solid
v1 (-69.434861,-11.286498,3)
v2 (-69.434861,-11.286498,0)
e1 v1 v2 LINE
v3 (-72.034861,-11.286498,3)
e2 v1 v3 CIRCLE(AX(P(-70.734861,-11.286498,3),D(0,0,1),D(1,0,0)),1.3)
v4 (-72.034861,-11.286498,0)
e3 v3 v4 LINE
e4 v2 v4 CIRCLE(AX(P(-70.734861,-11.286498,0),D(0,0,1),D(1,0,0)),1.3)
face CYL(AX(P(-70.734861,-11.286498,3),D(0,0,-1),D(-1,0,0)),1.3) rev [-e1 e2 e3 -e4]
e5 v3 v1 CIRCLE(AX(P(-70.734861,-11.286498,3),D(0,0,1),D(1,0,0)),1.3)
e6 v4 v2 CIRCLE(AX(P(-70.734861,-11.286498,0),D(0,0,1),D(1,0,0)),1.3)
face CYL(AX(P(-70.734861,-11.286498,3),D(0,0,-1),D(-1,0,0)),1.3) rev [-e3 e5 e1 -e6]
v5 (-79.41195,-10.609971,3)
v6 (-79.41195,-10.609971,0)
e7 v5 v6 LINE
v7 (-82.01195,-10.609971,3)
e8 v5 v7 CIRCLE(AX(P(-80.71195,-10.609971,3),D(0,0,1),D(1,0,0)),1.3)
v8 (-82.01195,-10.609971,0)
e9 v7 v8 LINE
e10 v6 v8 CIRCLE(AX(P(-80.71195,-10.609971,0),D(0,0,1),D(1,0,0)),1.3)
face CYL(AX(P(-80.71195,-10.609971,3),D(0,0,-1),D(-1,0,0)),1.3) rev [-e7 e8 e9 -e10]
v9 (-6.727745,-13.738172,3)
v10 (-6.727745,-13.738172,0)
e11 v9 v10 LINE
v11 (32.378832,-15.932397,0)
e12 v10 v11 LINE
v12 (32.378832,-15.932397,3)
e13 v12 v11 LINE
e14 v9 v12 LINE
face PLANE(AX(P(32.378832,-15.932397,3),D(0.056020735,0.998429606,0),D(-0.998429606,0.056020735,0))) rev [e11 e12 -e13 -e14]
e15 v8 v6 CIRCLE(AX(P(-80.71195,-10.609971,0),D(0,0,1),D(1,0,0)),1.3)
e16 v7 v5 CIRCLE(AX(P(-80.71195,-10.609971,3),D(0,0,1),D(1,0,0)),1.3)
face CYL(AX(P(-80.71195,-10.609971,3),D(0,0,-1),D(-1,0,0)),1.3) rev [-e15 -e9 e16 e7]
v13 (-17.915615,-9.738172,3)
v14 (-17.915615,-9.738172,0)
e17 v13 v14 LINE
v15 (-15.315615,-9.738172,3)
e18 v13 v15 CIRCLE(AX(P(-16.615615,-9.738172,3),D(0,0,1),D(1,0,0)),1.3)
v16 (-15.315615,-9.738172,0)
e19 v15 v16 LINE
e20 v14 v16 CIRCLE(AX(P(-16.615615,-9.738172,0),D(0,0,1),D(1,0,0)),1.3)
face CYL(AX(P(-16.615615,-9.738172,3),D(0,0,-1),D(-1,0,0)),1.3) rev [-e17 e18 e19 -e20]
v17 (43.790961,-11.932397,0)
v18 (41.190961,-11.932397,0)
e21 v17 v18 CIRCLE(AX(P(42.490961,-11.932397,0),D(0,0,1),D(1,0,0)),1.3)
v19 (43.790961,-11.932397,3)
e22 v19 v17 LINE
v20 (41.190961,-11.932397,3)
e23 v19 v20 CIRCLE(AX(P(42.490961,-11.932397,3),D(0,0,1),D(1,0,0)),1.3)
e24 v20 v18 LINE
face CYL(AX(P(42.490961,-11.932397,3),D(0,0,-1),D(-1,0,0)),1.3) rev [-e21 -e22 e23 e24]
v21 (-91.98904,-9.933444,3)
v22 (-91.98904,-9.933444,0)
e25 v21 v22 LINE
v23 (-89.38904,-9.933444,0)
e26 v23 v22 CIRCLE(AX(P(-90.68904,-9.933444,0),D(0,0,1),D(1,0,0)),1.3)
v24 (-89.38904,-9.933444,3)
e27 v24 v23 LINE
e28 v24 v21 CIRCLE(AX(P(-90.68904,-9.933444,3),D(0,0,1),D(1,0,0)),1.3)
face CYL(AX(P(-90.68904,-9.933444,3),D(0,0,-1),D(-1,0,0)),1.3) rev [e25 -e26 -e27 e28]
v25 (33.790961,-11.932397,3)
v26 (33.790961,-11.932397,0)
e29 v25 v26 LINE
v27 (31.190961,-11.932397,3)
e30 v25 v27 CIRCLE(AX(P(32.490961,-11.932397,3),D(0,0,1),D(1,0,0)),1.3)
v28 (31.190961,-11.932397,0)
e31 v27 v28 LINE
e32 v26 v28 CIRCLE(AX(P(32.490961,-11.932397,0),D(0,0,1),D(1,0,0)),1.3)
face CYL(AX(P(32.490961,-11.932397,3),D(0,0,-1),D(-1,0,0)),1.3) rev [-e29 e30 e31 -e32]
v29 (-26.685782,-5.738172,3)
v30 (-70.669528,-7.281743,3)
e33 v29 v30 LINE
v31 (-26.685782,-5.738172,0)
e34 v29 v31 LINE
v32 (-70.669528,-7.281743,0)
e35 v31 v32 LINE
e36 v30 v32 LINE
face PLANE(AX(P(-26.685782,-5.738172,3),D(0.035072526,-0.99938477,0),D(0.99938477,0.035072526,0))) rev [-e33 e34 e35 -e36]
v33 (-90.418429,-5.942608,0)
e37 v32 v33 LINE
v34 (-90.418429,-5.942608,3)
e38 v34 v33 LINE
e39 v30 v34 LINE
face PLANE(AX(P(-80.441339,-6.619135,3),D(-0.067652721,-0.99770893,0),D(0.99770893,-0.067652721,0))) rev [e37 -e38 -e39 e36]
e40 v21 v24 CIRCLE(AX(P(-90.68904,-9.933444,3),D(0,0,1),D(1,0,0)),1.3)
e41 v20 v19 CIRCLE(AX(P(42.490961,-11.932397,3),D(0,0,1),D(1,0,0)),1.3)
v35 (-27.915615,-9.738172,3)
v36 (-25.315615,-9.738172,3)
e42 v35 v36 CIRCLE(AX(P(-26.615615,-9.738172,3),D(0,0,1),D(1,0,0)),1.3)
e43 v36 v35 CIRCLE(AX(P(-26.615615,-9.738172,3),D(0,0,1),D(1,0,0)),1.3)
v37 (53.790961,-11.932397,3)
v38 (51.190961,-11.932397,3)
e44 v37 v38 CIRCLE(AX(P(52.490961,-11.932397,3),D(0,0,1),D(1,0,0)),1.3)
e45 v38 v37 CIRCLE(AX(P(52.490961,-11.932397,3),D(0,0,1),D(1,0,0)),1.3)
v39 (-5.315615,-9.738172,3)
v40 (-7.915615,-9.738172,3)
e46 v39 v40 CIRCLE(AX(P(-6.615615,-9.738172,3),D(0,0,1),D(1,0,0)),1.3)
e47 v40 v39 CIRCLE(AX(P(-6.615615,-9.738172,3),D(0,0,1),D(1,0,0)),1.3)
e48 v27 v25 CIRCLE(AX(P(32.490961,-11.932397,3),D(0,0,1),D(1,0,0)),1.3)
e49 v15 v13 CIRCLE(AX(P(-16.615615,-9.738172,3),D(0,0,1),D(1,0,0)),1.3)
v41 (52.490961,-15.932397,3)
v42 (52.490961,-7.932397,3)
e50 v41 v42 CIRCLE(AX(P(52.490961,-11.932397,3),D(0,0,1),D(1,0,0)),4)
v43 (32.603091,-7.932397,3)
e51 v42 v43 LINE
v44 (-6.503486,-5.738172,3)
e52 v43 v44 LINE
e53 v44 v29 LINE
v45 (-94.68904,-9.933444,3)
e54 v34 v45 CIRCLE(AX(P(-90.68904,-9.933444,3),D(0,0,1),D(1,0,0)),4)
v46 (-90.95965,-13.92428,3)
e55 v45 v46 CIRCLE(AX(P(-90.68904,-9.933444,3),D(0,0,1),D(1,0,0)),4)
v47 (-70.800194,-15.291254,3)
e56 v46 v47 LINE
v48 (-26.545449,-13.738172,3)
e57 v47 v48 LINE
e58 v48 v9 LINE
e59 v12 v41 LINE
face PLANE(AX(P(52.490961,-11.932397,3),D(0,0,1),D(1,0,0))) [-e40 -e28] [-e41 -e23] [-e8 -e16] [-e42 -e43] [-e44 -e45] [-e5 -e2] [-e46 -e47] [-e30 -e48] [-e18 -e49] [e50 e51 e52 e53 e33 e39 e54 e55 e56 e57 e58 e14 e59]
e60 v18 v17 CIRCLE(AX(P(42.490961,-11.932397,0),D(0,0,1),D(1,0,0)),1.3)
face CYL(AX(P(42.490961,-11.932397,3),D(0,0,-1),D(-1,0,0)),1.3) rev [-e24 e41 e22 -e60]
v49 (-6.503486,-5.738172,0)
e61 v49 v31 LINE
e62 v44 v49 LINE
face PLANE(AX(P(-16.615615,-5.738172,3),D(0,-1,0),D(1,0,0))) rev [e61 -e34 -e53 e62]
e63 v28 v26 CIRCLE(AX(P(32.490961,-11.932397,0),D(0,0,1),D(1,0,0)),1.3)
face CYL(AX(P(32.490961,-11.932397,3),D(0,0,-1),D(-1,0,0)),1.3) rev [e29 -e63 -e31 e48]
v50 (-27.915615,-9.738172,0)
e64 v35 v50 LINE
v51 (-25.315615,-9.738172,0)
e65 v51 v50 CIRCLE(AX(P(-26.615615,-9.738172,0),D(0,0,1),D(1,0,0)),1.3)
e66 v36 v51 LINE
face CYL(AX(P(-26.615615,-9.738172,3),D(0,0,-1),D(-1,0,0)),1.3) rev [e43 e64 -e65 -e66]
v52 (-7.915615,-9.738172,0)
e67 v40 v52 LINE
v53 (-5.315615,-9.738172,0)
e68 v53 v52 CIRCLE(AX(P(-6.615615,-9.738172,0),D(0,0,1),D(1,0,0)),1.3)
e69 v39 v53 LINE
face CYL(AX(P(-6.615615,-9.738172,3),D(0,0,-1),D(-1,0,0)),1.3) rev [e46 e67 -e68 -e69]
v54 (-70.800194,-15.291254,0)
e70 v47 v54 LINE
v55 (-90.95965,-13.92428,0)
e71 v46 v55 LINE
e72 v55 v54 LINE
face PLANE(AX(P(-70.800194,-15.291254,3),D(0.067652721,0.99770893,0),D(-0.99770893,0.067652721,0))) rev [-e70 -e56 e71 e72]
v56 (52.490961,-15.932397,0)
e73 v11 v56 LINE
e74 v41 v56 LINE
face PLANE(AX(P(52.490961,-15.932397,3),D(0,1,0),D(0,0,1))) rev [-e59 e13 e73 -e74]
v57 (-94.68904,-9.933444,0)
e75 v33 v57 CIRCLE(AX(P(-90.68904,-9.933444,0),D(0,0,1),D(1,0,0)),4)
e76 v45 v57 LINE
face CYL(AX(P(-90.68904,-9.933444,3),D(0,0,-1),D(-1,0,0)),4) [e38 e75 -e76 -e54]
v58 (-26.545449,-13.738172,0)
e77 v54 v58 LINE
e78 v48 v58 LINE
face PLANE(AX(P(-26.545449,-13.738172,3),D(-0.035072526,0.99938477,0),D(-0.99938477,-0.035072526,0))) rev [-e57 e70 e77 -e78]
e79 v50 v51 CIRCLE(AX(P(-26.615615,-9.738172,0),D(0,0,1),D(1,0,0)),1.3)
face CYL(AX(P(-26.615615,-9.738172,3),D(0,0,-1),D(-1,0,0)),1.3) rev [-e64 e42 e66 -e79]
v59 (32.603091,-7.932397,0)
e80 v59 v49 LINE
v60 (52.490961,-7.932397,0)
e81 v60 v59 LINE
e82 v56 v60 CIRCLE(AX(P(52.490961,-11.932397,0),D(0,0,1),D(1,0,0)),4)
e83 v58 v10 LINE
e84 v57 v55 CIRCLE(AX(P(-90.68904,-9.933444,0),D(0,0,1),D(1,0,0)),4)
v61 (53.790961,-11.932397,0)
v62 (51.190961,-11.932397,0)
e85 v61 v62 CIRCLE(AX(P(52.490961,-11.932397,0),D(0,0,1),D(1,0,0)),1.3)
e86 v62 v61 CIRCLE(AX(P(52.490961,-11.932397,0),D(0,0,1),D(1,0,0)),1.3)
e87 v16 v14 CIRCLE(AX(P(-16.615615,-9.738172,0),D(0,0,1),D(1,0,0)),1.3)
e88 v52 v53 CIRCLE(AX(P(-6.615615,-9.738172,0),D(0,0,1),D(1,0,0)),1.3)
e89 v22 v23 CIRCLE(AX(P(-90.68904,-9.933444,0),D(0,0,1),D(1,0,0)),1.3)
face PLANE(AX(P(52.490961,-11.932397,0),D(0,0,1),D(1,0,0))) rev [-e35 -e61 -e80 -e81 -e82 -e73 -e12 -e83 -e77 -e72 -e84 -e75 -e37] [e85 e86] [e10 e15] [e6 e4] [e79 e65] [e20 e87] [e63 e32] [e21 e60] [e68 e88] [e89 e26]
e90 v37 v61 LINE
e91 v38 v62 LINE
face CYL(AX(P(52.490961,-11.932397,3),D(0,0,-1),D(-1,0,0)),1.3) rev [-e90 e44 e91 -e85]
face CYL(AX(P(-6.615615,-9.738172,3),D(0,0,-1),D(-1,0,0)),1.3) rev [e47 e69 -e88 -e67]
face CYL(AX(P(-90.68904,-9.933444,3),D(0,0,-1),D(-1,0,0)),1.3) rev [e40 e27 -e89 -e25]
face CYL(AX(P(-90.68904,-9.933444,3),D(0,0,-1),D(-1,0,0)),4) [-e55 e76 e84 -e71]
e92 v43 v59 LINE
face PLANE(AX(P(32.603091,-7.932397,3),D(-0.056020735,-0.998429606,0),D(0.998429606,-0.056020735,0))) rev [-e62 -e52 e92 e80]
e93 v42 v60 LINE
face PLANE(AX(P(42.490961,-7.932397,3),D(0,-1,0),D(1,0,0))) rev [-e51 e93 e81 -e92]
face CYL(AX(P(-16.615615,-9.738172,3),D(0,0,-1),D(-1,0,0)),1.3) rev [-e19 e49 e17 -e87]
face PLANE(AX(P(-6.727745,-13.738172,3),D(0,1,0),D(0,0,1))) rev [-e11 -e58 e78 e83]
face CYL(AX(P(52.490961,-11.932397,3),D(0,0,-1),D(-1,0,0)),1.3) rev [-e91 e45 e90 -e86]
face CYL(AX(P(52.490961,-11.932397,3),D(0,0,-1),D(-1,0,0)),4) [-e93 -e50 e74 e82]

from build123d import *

# Parameters (mm, degrees)
SKETCH3_R           = 1.3
SKETCH3_R_2         = 1.299999997
SKETCH3_R_3         = 1.299999994
SKETCH3_R_4         = 1.299999992
BOSS_EXTRUDE4_DEPTH = 3


with BuildPart() as part:
    # Sketch3 → Boss-Extrude4 (new body)
    with BuildSketch(Plane.XY):
        with BuildLine():
            Line((52.490961286, -7.932397294), (42.490961286, -7.932397294))
            Line((42.490961286, -7.932397294), (32.603090799, -7.932397294))
            Line((32.603090799, -7.932397294), (-6.503485734, -5.738172333))
            Line((-6.503485734, -5.738172333), (-16.615615248, -5.738172333))
            Line((-16.615615248, -5.738172333), (-26.685781884, -5.738172333))
            Line((-26.685781884, -5.738172333), (-70.669528111, -7.281743071))
            Line((-70.669528111, -7.281743071), (-80.441339321, -6.619135373))
            Line((-80.441339321, -6.619135373), (-90.418428622, -5.942608164))
            ThreePointArc((-90.418428622, -5.942608164), (-94.679875227, -9.662833001), (-90.95965039, -13.924279606))
            Line((-90.95965039, -13.924279606), (-80.982561088, -14.600806815))
            Line((-80.982561088, -14.600806815), (-70.800193694, -15.291253536))
            Line((-70.800193694, -15.291253536), (-26.545448611, -13.738172333))
            Line((-26.545448611, -13.738172333), (-16.615615248, -13.738172333))
            Line((-16.615615248, -13.738172333), (-6.727744762, -13.738172333))
            Line((-6.727744762, -13.738172333), (32.378831772, -15.932397294))
            Line((32.378831772, -15.932397294), (42.490961286, -15.932397294))
            Line((42.490961286, -15.932397294), (52.490961286, -15.932397294))
            ThreePointArc((52.490961286, -15.932397294), (56.490961286, -11.932397294), (52.490961286, -7.932397294))
        make_face()
        with Locations((-90.689039506, -9.933443885)):
            Circle(SKETCH3_R, mode=Mode.SUBTRACT)
        with Locations((-70.734860903, -11.286498303)):
            Circle(SKETCH3_R, mode=Mode.SUBTRACT)
        with Locations((-80.711950204, -10.609971094)):
            Circle(SKETCH3_R, mode=Mode.SUBTRACT)
        with Locations((-26.615615248, -9.738172333)):
            Circle(SKETCH3_R, mode=Mode.SUBTRACT)
        with Locations((-16.615615248, -9.738172333)):
            Circle(SKETCH3_R_2, mode=Mode.SUBTRACT)
        with Locations((-6.615615248, -9.738172333)):
            Circle(SKETCH3_R_3, mode=Mode.SUBTRACT)
        with Locations((32.490961286, -11.932397294)):
            Circle(SKETCH3_R_3, mode=Mode.SUBTRACT)
        with Locations((42.490961286, -11.932397294)):
            Circle(SKETCH3_R_4, mode=Mode.SUBTRACT)
        with Locations((52.490961286, -11.932397294)):
            Circle(SKETCH3_R, mode=Mode.SUBTRACT)
    extrude(amount=BOSS_EXTRUDE4_DEPTH)


solid = part.part
